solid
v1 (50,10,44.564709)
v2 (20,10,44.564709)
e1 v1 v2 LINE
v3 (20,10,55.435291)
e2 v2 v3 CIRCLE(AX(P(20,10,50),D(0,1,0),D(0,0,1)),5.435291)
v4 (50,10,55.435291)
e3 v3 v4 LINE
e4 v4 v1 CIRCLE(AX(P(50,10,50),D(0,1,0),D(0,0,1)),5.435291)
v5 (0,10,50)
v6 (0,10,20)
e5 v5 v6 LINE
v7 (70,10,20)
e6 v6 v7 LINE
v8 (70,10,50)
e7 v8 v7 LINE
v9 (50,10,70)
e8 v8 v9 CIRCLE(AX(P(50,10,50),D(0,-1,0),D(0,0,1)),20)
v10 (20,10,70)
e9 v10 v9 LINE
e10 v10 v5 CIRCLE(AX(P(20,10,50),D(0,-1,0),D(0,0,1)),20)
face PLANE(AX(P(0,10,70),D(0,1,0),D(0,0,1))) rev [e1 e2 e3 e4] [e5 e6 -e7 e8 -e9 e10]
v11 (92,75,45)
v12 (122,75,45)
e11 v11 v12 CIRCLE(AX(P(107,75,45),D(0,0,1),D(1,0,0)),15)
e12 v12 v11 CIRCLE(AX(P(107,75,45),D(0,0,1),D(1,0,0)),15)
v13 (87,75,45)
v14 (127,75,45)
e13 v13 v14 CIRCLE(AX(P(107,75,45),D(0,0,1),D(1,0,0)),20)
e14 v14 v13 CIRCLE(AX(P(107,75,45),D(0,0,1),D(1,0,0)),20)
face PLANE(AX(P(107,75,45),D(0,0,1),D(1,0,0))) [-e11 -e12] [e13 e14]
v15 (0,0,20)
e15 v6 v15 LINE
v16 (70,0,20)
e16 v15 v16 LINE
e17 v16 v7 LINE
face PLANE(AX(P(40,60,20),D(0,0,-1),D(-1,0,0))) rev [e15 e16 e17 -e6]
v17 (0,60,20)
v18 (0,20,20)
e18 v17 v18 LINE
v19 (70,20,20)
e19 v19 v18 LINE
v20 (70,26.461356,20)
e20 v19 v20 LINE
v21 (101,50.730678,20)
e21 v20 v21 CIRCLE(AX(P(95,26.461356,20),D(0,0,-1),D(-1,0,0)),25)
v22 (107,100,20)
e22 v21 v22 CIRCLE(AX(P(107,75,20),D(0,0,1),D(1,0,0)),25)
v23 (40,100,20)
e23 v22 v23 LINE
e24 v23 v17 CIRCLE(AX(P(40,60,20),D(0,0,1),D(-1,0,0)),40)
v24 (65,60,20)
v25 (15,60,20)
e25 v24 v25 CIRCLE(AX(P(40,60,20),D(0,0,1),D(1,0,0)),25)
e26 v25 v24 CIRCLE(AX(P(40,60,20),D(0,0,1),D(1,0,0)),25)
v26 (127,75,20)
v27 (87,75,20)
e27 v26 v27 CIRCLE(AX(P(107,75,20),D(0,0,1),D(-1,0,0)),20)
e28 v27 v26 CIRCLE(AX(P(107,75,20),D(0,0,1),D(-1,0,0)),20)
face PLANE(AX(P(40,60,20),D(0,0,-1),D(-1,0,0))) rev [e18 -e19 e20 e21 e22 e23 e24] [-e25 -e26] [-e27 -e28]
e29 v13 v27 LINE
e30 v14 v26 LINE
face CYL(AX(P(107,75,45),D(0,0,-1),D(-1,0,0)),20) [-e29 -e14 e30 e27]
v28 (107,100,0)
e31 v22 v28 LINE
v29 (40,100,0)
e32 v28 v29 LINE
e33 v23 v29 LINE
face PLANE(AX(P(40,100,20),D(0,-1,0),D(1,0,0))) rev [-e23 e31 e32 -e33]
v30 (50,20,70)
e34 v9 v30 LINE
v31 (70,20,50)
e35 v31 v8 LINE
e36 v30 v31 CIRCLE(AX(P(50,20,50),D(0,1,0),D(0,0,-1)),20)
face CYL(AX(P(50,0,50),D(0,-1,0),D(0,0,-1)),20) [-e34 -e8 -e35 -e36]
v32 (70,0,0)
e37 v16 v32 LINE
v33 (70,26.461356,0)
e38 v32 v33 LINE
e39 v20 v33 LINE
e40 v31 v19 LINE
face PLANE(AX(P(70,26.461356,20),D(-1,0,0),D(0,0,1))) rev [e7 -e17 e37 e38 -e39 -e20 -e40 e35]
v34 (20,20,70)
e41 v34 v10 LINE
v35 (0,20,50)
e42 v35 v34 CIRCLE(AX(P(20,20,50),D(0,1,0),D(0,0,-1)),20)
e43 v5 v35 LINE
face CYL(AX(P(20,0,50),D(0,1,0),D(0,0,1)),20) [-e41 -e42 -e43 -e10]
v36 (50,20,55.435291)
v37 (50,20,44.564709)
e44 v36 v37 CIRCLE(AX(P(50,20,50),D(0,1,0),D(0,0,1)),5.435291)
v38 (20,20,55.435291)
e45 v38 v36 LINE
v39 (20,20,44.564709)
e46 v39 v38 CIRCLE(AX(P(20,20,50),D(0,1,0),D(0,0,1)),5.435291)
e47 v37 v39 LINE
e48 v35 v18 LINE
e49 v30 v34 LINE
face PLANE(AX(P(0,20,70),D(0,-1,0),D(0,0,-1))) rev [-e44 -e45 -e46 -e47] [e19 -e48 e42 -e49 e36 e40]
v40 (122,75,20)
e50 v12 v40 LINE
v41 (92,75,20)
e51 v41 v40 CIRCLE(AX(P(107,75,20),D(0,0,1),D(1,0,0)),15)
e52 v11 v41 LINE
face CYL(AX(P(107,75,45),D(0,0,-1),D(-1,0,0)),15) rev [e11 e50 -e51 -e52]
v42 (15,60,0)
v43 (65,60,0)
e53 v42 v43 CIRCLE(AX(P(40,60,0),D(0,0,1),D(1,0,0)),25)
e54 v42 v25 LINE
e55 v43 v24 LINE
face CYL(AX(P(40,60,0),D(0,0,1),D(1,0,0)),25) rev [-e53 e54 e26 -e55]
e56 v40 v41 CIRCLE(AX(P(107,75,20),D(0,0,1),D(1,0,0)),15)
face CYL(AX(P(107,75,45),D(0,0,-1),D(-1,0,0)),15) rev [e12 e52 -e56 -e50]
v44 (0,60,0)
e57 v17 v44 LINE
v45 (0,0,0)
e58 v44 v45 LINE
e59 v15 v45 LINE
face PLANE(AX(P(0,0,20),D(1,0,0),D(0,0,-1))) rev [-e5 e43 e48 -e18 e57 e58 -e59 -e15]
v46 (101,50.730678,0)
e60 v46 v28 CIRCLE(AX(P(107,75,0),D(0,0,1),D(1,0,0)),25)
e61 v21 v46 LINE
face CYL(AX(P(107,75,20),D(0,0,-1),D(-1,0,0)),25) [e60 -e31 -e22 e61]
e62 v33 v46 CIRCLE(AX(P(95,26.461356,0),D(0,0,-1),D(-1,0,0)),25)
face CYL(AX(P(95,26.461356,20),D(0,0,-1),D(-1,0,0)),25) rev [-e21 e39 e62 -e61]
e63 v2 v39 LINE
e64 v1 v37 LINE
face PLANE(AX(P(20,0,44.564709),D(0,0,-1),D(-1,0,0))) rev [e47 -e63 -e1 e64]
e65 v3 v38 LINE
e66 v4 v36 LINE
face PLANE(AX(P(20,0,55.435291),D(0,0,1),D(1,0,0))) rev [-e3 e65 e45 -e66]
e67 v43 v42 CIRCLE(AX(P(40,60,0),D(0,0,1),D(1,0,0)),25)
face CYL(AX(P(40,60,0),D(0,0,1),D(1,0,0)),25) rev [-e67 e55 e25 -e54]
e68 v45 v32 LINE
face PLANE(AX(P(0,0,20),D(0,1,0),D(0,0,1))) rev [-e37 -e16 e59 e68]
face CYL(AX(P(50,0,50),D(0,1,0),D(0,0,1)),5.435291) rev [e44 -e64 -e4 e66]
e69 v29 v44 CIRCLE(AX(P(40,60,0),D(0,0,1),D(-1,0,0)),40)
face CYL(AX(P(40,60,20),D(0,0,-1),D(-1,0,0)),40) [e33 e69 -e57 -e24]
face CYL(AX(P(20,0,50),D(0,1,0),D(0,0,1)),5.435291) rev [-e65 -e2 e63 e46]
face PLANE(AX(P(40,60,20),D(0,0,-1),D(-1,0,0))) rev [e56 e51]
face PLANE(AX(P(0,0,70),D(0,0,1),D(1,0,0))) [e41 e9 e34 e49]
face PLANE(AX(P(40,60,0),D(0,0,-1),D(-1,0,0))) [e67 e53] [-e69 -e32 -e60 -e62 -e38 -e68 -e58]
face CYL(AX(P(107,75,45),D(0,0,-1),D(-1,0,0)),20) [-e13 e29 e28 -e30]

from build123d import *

# Parameters (mm, degrees)
UPRIGHT_PLATE_DEPTH             = 20
BEARING_BOSS_PROFILE_R          = 20
BEARING_BOSS_PROFILE_R_2        = 15
BEARING_BOSS_DEPTH              = 25
BEARING_BORE_SKETCH_R           = 25
BEARING_BORE_50_DEPTH           = 168.478356811
BASE_PLATE_PROFILE_W            = 70
BASE_PLATE_PROFILE_H            = 10
BASE_PLATE_DEPTH                = 50
BASE_PLATE_CORNER_FILLETS_R20_R = 20
MOUNTING_SLOT_DEPTH             = 170.481562419


with BuildPart() as part:
    # Upright Plate Profile → Upright Plate (new body)
    with BuildSketch(Plane.XY):
        with BuildLine():
            Line((0, 0), (70, 0))
            Line((70, 0), (70, 26.461355602))
            ThreePointArc((70, 26.461355602), (79.588964993, 46.146375287), (101, 50.730677801))
            ThreePointArc((101, 50.730677801), (131.816658266, 71.977836452), (107, 100))
            Line((107, 100), (40, 100))
            ThreePointArc((40, 100), (11.715728753, 88.284271247), (0, 60))
            Line((0, 60), (0, 0))
        make_face()
    extrude(amount=UPRIGHT_PLATE_DEPTH)

    # Bearing Boss Profile → Bearing Boss (add)
    with BuildSketch(Plane.XY.offset(20)):
        with Locations(Location((107, 75, 0), (0, 0, 180))):
            Circle(BEARING_BOSS_PROFILE_R)
        with Locations((107, 75)):
            Circle(BEARING_BOSS_PROFILE_R_2, mode=Mode.SUBTRACT)
    extrude(amount=BEARING_BOSS_DEPTH)

    # Bearing Bore Sketch → Bearing Bore Ø50 (cut, through all)
    with BuildSketch(Plane.XY.offset(20)):
        with Locations((40, 60)):
            Circle(BEARING_BORE_SKETCH_R)
    extrude(amount=-BEARING_BORE_50_DEPTH, mode=Mode.SUBTRACT)

    # Base Plate Profile → Base Plate (add)
    with BuildSketch(Plane.XY.offset(20)):
        with Locations((35, 15)):
            Rectangle(BASE_PLATE_PROFILE_W, BASE_PLATE_PROFILE_H)
    extrude(amount=BASE_PLATE_DEPTH)

    # Base Plate Corner Fillets R20
    base_plate_corner_fillets_r20_edges = [part.edges().sort_by_distance(p)[0] for p in [
        (70, 15, 70),
        (0, 15, 70),
    ]]
    fillet(base_plate_corner_fillets_r20_edges, radius=BASE_PLATE_CORNER_FILLETS_R20_R)

    # Mounting Slot Sketch → Mounting Slot (cut, through all)
    with BuildSketch(Plane(origin=(0, 20, 0), x_dir=(1, 0, 0), z_dir=(0, 1, 0))):
        with BuildLine():
            Line((20, -44.564709442), (50, -44.564709442))
            ThreePointArc((50, -44.564709442), (55.435290558, -50), (50, -55.435290558))
            Line((50, -55.435290558), (20, -55.435290558))
            ThreePointArc((20, -55.435290558), (14.564709442, -50), (20, -44.564709442))
        make_face()
    extrude(amount=-MOUNTING_SLOT_DEPTH, mode=Mode.SUBTRACT)


solid = part.part
